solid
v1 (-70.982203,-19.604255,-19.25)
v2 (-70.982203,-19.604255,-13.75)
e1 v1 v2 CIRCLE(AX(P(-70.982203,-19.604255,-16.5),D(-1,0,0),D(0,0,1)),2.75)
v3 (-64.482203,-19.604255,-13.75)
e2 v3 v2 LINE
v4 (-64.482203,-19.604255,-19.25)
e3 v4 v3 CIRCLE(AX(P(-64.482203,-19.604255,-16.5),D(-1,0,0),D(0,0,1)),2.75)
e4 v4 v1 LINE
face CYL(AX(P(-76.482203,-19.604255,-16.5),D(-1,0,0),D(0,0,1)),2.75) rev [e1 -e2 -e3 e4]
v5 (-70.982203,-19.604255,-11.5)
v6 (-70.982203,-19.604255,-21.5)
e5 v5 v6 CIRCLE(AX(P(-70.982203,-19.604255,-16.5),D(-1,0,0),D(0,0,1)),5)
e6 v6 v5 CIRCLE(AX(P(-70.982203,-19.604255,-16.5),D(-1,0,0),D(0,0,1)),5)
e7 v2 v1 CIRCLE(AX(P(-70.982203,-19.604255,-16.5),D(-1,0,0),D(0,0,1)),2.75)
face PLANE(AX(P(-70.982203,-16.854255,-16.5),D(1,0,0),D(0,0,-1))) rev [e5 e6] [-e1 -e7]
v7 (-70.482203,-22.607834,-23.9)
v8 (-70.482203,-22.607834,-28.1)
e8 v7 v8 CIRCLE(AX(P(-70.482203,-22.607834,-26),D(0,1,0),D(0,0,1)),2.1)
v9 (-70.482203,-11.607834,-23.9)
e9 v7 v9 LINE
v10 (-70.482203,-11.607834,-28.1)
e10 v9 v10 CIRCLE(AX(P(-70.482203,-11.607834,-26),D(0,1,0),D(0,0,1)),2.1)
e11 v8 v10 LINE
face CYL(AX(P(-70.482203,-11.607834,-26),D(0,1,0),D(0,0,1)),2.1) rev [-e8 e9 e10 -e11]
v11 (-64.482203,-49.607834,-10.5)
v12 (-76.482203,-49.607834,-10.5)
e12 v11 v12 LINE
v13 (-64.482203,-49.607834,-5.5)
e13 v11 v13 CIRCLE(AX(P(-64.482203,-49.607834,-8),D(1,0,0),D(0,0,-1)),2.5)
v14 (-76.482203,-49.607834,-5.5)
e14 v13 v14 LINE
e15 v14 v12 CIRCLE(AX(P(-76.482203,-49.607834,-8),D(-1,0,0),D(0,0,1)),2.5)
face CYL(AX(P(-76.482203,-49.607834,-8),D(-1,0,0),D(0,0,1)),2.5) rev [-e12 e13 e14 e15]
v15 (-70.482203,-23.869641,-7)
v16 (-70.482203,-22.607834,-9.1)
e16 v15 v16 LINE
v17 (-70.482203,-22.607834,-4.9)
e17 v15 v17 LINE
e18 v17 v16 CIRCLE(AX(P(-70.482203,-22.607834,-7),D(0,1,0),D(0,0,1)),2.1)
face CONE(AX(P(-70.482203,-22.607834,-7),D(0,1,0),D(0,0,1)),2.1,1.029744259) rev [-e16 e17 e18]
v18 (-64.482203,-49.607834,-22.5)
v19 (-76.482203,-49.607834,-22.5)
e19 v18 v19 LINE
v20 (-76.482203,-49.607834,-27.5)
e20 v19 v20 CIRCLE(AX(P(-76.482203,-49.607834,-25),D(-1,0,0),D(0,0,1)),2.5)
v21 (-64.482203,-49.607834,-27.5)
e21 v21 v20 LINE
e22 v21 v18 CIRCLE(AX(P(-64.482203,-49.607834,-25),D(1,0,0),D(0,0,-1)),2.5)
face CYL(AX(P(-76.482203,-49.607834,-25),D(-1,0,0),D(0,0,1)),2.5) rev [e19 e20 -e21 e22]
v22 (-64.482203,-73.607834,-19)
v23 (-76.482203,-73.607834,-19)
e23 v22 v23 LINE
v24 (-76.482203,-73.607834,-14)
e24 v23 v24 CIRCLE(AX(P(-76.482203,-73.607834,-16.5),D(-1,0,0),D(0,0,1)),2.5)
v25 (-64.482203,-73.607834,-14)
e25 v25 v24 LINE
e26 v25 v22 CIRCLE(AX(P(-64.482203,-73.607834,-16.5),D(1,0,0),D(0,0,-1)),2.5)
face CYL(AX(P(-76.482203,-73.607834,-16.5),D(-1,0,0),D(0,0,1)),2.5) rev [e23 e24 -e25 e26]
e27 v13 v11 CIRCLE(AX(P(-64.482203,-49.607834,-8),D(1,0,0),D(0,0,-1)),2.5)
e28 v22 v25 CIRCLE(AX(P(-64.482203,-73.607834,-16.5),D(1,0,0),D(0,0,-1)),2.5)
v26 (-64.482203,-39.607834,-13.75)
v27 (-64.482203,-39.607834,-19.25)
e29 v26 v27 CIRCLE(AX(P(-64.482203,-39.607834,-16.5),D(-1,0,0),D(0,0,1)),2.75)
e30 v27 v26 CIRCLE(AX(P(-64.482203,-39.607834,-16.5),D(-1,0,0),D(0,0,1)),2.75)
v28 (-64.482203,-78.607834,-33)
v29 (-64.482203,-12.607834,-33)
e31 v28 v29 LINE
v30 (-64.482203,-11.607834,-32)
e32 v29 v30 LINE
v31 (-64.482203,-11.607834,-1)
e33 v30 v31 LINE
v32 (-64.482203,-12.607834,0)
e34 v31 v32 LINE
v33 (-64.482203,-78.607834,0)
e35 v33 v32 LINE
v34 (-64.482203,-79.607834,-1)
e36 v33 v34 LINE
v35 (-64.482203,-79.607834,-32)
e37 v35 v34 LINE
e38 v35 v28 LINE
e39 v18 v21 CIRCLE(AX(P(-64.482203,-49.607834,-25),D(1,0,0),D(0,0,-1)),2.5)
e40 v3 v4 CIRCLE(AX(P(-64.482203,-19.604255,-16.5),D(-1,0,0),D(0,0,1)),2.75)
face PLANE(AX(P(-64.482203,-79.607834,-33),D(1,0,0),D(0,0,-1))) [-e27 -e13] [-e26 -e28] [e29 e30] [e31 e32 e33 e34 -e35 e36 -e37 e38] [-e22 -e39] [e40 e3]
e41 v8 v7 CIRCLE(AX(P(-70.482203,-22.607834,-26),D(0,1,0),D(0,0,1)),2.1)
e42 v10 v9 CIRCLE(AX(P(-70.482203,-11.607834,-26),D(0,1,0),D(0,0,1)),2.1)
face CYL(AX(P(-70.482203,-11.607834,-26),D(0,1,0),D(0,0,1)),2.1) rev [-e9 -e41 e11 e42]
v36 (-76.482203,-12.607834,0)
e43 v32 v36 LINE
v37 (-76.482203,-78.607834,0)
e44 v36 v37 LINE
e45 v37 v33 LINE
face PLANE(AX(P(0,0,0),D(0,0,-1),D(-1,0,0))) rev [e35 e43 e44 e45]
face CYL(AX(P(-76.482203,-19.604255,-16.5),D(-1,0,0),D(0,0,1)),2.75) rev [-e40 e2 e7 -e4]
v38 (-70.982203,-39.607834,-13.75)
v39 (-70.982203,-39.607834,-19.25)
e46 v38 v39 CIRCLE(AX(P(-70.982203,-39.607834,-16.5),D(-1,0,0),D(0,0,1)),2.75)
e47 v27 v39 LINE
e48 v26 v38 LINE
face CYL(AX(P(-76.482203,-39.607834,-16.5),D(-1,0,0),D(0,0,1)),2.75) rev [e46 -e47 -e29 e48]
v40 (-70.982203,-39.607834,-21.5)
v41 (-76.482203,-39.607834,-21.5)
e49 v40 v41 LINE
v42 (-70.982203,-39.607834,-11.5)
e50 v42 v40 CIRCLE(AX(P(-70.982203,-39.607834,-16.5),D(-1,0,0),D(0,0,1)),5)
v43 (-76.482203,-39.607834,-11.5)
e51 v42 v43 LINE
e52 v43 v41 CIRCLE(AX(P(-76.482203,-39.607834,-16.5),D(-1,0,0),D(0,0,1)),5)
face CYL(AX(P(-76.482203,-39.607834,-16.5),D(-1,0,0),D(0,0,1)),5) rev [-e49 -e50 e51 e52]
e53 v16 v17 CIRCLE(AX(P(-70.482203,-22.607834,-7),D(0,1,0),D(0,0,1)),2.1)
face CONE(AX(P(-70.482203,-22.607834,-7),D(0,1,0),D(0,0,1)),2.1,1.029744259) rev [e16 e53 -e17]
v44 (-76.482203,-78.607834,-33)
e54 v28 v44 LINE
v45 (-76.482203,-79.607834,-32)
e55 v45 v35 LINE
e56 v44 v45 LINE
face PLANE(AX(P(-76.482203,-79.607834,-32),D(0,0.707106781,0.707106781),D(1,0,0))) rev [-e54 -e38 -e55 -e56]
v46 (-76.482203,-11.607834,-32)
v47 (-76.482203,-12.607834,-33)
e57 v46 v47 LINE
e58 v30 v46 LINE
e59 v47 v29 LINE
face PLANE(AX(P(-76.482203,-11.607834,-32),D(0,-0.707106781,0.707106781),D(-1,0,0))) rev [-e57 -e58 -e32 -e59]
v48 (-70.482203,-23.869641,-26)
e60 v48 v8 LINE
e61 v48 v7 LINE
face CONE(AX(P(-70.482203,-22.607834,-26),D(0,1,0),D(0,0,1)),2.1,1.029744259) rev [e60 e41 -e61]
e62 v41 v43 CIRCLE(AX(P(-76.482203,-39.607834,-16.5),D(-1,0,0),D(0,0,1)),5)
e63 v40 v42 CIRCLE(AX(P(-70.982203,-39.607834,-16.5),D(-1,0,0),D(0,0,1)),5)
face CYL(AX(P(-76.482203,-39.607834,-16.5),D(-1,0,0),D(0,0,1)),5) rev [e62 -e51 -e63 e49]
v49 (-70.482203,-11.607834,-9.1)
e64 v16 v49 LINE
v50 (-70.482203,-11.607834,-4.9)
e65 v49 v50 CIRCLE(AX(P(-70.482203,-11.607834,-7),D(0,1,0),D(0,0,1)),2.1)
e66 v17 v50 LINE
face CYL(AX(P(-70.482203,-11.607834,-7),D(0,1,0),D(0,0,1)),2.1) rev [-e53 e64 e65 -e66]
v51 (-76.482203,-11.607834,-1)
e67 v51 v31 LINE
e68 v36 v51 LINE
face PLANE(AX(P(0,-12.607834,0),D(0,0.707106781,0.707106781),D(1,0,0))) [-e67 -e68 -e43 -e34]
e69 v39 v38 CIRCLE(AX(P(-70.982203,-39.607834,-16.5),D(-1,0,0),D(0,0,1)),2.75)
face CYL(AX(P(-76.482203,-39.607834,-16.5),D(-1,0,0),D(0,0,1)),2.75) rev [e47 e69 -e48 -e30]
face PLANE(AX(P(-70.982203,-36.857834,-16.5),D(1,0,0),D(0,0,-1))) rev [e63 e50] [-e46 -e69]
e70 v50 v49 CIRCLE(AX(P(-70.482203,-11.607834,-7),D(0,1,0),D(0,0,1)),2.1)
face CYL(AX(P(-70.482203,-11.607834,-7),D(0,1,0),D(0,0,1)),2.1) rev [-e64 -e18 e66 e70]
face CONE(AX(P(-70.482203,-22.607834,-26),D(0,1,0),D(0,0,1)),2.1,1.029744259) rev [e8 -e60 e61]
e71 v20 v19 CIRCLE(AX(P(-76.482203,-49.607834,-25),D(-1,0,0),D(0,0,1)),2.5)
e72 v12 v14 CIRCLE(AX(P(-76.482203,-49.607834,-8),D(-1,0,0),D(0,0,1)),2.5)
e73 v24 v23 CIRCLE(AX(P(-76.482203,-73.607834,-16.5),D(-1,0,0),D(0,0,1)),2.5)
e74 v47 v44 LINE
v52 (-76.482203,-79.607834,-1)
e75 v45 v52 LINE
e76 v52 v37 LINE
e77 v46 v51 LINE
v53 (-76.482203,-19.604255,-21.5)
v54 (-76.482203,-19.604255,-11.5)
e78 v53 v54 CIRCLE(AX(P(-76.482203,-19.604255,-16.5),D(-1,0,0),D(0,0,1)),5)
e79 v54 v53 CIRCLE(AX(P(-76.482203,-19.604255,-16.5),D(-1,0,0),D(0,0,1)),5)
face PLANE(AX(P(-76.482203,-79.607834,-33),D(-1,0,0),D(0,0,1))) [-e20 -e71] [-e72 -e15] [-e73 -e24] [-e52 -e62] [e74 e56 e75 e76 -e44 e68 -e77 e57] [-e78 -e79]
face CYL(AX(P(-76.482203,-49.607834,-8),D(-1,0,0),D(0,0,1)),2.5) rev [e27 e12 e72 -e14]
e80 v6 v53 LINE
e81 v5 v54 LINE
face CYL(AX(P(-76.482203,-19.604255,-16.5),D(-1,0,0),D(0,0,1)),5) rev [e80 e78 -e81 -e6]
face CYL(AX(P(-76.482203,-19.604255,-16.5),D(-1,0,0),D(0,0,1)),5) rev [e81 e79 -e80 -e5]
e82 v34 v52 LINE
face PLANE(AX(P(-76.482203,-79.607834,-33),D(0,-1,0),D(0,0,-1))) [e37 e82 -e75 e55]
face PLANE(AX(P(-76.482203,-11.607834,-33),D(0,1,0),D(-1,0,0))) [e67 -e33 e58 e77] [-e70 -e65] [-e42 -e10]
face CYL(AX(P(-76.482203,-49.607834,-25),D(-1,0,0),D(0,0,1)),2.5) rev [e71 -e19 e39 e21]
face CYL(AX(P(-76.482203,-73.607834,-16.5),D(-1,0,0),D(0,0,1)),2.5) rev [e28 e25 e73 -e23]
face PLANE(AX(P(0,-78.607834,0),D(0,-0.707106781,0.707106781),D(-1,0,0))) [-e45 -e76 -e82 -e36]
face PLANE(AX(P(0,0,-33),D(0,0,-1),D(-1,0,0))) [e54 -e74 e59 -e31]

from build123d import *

# Parameters (mm, degrees)
SKETCH_1_W                  = 12
SKETCH_1_H                  = 68
EXTRUDE_1_DEPTH             = 33
HOLE_WIZARD_M6_1_D          = 5
HOLE_WIZARD_M6_1_DEPTH      = 15
HOLE_WIZARD_M6_1_TIP        = 1.502151548
HOLE_WIZARD_M5_1_D          = 4.2
HOLE_WIZARD_M5_1_DEPTH      = 11
HOLE_WIZARD_M5_1_TIP        = 1.2618073
HOLE_WIZARD_C_0_D           = 5.5
HOLE_WIZARD_C_0_CBORE_D     = 10
HOLE_WIZARD_C_0_CBORE_DEPTH = 5.5
CHAMFER_1_SIZE              = 1


with BuildPart() as part:
    # 草图1 → 凸台-拉伸1 (new body)
    with BuildSketch(Plane.XY):
        with Locations((-70.482202682, -45.607833778)):
            Rectangle(SKETCH_1_W, SKETCH_1_H)
    extrude(amount=-EXTRUDE_1_DEPTH)

    # M6 螺纹孔1
    with Locations(Plane.ZY.offset(76.482202682)):
        with Locations((-16.5, -73.607833778), (-8, -49.607833778), (-25, -49.607833778)):
            Hole(HOLE_WIZARD_M6_1_D / 2, depth=HOLE_WIZARD_M6_1_DEPTH)
            with Locations((0, 0, -(HOLE_WIZARD_M6_1_DEPTH + HOLE_WIZARD_M6_1_TIP / 2))):  # 118° drill point
                Cone(0, HOLE_WIZARD_M6_1_D / 2, HOLE_WIZARD_M6_1_TIP, mode=Mode.SUBTRACT)

    # M5 螺纹孔1
    with Locations(Plane(origin=(0, -11.607833778, 0), x_dir=(1, 0, 0), z_dir=(0, 1, 0))):
        with Locations((-70.482202682, 26), (-70.482202682, 7)):
            Hole(HOLE_WIZARD_M5_1_D / 2, depth=HOLE_WIZARD_M5_1_DEPTH)
            with Locations((0, 0, -(HOLE_WIZARD_M5_1_DEPTH + HOLE_WIZARD_M5_1_TIP / 2))):  # 118° drill point
                Cone(0, HOLE_WIZARD_M5_1_D / 2, HOLE_WIZARD_M5_1_TIP, mode=Mode.SUBTRACT)

    # 打孔尺寸根据六角头螺栓 C 级的类型0 (through all)
    with Locations(Plane.ZY.offset(76.482202682)):
        with Locations((-16.5, -19.604255019), (-16.5, -39.607833778)):
            CounterBoreHole(HOLE_WIZARD_C_0_D / 2, HOLE_WIZARD_C_0_CBORE_D / 2, HOLE_WIZARD_C_0_CBORE_DEPTH)

    # 倒角1
    chamfer_1_edges = [part.edges().sort_by_distance(p)[0] for p in [
        (-70.482202682, -11.607833778, -33),
        (-70.482202682, -11.607833778, 0),
        (-70.482202682, -79.607833778, 0),
        (-70.482202682, -79.607833778, -33),
    ]]
    chamfer(chamfer_1_edges, length=CHAMFER_1_SIZE)


solid = part.part
